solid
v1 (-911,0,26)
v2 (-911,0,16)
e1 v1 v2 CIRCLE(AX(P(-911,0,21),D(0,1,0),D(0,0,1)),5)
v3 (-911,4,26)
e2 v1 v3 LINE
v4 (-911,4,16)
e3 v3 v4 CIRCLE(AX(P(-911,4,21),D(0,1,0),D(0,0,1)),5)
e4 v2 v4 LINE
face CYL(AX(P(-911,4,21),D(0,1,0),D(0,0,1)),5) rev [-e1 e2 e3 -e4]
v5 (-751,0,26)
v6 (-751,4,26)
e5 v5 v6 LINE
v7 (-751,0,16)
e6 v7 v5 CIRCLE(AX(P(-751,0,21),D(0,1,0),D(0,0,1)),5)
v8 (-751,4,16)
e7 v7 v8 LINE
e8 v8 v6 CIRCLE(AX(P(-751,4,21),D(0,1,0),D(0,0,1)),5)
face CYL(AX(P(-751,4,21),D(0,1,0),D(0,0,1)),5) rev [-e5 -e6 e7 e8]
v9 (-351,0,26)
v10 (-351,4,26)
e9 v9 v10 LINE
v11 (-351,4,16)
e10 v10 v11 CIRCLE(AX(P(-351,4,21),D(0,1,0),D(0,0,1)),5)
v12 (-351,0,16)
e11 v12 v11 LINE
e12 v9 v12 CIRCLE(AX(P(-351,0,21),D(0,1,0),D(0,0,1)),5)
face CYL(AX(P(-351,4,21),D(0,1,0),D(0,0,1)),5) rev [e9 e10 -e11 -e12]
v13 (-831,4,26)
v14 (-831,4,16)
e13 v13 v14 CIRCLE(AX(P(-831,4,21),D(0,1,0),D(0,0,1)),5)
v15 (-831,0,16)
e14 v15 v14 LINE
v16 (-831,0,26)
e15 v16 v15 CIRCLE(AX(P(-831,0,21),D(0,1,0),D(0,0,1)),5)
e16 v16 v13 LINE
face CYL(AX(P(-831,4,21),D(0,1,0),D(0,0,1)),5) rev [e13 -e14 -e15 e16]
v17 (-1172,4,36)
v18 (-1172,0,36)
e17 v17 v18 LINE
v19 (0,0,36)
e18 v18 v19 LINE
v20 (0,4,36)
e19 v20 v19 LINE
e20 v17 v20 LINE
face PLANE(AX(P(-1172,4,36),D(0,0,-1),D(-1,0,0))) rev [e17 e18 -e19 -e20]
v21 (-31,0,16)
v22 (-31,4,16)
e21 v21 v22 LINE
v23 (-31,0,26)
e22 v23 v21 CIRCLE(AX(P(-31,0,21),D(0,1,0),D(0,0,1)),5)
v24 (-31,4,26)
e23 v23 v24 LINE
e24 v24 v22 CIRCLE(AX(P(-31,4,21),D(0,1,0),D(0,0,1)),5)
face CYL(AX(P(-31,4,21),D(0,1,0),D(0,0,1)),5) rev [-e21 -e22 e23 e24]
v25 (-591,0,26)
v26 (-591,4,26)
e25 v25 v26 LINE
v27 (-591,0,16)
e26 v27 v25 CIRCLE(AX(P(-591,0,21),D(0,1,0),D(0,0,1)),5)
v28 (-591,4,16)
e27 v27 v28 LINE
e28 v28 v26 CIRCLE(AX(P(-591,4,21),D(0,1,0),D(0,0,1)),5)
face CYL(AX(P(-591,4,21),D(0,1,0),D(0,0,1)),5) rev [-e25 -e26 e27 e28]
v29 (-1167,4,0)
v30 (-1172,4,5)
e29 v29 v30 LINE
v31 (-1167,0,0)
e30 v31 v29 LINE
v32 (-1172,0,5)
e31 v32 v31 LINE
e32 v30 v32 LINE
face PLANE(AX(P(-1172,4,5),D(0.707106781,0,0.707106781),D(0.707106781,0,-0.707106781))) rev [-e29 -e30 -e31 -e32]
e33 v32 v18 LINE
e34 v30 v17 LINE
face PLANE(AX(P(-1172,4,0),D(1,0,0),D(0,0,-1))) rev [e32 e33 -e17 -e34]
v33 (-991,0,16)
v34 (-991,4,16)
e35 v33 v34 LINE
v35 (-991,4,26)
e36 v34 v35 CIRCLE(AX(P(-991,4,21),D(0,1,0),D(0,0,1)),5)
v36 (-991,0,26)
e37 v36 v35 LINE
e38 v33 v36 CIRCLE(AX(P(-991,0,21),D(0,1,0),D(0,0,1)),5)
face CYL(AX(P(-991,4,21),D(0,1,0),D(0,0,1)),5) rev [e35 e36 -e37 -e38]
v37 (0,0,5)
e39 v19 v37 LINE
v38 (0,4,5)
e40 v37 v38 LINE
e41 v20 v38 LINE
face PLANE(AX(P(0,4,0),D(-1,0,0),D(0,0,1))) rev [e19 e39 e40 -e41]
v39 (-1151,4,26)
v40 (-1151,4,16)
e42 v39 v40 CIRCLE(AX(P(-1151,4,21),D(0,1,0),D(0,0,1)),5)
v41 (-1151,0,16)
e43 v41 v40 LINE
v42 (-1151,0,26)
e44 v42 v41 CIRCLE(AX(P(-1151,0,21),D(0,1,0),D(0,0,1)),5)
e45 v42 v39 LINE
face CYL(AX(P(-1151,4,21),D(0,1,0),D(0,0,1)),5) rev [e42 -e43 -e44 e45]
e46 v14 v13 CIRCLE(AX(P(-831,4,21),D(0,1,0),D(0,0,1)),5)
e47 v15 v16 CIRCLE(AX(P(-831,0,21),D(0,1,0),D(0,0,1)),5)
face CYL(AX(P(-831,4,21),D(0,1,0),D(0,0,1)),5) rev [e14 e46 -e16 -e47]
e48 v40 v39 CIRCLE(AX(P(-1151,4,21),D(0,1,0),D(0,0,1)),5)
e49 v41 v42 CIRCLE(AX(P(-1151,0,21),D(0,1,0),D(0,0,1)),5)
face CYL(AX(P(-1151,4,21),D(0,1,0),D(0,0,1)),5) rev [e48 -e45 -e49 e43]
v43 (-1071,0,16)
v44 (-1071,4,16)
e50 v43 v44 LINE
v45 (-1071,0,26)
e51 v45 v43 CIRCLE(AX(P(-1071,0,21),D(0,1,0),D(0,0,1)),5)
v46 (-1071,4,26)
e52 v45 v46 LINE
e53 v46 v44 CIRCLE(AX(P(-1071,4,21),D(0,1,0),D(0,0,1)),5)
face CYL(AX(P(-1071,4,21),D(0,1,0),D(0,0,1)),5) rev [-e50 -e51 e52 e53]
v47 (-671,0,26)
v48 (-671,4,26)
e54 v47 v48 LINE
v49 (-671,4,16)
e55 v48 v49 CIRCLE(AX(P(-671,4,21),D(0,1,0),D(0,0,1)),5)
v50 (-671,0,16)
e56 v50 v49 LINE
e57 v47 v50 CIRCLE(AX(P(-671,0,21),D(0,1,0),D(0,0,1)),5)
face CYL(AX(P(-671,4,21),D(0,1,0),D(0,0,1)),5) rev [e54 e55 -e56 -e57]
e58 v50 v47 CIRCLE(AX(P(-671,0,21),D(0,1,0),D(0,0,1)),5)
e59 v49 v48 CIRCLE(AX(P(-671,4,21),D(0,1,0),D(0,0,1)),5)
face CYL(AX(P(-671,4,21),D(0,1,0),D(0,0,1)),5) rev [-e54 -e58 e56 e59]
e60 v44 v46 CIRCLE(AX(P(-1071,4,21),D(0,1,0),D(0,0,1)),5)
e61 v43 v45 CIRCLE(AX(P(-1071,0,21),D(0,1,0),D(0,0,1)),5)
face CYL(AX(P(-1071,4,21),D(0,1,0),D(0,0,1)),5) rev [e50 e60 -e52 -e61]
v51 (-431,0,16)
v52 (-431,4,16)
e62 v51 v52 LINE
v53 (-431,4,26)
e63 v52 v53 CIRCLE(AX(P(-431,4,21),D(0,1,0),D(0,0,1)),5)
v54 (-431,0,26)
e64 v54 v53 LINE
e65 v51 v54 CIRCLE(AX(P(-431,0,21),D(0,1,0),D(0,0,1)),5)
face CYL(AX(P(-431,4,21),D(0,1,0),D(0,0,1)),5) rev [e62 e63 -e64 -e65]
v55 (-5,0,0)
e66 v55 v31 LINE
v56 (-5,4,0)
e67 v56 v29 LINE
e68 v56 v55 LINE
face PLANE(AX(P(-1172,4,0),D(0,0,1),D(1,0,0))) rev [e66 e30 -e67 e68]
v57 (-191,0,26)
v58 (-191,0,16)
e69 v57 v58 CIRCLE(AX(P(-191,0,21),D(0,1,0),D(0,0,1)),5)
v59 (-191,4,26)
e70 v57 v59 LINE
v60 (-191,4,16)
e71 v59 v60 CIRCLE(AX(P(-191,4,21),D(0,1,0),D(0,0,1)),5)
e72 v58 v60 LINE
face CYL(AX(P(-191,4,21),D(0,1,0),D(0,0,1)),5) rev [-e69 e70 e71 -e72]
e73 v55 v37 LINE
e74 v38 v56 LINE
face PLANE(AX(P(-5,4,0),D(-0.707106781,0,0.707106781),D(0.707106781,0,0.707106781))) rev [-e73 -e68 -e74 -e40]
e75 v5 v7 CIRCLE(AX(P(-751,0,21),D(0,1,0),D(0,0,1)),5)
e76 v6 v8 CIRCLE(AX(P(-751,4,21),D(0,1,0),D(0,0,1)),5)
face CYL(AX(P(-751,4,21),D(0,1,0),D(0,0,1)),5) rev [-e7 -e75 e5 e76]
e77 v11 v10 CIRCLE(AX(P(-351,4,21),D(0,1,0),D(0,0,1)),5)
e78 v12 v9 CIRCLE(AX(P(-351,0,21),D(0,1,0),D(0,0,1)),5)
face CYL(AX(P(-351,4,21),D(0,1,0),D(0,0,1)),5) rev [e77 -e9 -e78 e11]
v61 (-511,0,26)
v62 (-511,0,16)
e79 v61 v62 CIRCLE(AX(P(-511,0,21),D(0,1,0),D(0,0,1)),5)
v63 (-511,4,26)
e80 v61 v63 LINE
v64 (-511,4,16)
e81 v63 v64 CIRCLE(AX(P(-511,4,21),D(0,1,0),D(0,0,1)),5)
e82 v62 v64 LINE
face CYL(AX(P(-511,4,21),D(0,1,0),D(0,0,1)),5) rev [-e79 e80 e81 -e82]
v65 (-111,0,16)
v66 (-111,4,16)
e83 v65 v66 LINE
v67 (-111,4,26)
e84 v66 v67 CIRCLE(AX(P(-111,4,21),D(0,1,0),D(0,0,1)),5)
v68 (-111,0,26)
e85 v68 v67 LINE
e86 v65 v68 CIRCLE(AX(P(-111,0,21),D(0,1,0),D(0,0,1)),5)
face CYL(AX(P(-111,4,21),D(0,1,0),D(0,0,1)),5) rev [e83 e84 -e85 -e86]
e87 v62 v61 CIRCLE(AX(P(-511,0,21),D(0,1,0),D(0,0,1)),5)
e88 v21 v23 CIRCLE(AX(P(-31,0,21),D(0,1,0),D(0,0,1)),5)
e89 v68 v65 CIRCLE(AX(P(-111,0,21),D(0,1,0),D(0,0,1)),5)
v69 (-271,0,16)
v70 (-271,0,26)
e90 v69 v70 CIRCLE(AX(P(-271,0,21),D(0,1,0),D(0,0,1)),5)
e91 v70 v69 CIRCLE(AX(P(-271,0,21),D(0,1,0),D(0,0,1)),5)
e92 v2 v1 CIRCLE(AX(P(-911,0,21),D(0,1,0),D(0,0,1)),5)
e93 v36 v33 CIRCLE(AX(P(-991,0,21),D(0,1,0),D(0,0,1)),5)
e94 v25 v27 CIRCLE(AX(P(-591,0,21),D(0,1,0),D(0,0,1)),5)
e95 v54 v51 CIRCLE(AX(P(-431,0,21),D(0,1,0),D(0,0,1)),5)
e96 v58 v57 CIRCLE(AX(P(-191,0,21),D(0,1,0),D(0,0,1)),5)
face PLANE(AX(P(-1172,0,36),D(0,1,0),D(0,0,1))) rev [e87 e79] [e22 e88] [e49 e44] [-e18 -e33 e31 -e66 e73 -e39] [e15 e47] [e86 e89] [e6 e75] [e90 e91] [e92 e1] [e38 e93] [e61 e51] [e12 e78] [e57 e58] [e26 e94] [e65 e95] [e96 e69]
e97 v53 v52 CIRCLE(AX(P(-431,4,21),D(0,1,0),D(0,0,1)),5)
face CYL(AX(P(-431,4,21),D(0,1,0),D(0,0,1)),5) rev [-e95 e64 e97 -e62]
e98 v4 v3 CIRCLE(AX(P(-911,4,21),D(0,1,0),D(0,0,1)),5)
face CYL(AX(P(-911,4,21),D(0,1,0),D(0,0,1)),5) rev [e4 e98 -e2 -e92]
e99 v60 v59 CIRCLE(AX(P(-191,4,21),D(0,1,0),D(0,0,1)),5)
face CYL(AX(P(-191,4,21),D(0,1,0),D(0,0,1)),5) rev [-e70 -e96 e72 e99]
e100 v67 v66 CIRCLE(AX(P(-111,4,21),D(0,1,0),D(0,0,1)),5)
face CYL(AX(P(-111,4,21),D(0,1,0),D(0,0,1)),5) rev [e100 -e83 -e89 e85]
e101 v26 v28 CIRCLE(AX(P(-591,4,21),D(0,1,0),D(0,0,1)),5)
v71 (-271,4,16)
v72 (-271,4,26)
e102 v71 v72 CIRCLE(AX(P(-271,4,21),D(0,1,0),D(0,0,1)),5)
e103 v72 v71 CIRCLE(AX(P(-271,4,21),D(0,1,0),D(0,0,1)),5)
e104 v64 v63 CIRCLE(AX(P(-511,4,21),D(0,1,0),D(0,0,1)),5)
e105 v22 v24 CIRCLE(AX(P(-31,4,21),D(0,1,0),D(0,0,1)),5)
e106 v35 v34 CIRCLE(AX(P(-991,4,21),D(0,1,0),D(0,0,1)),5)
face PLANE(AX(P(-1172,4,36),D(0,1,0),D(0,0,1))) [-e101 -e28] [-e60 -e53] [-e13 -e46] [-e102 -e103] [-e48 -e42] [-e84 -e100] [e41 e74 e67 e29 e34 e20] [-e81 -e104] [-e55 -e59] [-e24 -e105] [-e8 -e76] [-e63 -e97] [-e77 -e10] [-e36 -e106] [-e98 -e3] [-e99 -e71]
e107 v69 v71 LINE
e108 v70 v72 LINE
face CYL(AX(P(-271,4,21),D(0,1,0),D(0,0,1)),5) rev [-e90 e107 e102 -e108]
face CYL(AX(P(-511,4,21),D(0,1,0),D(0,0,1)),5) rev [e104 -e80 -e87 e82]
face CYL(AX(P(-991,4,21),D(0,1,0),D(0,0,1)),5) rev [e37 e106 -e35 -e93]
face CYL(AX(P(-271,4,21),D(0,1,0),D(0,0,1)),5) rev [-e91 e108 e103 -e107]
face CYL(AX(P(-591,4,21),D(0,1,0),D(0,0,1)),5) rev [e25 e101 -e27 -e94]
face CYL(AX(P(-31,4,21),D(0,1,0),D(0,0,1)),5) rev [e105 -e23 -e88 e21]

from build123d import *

# Parameters (mm, degrees)
SKETCH_1_W              = 1172
SKETCH_1_H              = 36
EXTRUDE_1_DEPTH         = 4
CHAMFER_1_SIZE          = 5
HOLE_WIZARD_10_0_10_1_D = 10
PATTERN_LINEAR_1_COUNT  = 15
PATTERN_LINEAR_1_PITCH  = 80


with BuildPart() as part:
    # 草图1 → 凸台-拉伸1 (new body)
    with BuildSketch(Plane(origin=(0, 0, 0), x_dir=(1, 0, 0), z_dir=(0, 1, 0))):
        with Locations((-586, -18)):
            Rectangle(SKETCH_1_W, SKETCH_1_H)
    extrude(amount=EXTRUDE_1_DEPTH)

    # 倒角1
    chamfer_1_edges = [part.edges().sort_by_distance(p)[0] for p in [
        (-1172, 2, 0),
        (0, 2, 0),
    ]]
    chamfer(chamfer_1_edges, length=CHAMFER_1_SIZE)

    # Ø10.0 (10) 直径孔1 (through all)
    with Locations(Plane(origin=(0, 4, 0), x_dir=(-1, 0, 0), z_dir=(0, 1, 0))):
        with Locations((1151, 21)):
            hole_wizard_10_0_10_1 = Hole(HOLE_WIZARD_10_0_10_1_D / 2)

    # 阵列(线性)1: Ø10.0 (10) 直径孔1 ×15
    with Locations(*[(i * PATTERN_LINEAR_1_PITCH, 0, 0) for i in range(1, PATTERN_LINEAR_1_COUNT)]):
        add(hole_wizard_10_0_10_1, mode=Mode.SUBTRACT)


solid = part.part
